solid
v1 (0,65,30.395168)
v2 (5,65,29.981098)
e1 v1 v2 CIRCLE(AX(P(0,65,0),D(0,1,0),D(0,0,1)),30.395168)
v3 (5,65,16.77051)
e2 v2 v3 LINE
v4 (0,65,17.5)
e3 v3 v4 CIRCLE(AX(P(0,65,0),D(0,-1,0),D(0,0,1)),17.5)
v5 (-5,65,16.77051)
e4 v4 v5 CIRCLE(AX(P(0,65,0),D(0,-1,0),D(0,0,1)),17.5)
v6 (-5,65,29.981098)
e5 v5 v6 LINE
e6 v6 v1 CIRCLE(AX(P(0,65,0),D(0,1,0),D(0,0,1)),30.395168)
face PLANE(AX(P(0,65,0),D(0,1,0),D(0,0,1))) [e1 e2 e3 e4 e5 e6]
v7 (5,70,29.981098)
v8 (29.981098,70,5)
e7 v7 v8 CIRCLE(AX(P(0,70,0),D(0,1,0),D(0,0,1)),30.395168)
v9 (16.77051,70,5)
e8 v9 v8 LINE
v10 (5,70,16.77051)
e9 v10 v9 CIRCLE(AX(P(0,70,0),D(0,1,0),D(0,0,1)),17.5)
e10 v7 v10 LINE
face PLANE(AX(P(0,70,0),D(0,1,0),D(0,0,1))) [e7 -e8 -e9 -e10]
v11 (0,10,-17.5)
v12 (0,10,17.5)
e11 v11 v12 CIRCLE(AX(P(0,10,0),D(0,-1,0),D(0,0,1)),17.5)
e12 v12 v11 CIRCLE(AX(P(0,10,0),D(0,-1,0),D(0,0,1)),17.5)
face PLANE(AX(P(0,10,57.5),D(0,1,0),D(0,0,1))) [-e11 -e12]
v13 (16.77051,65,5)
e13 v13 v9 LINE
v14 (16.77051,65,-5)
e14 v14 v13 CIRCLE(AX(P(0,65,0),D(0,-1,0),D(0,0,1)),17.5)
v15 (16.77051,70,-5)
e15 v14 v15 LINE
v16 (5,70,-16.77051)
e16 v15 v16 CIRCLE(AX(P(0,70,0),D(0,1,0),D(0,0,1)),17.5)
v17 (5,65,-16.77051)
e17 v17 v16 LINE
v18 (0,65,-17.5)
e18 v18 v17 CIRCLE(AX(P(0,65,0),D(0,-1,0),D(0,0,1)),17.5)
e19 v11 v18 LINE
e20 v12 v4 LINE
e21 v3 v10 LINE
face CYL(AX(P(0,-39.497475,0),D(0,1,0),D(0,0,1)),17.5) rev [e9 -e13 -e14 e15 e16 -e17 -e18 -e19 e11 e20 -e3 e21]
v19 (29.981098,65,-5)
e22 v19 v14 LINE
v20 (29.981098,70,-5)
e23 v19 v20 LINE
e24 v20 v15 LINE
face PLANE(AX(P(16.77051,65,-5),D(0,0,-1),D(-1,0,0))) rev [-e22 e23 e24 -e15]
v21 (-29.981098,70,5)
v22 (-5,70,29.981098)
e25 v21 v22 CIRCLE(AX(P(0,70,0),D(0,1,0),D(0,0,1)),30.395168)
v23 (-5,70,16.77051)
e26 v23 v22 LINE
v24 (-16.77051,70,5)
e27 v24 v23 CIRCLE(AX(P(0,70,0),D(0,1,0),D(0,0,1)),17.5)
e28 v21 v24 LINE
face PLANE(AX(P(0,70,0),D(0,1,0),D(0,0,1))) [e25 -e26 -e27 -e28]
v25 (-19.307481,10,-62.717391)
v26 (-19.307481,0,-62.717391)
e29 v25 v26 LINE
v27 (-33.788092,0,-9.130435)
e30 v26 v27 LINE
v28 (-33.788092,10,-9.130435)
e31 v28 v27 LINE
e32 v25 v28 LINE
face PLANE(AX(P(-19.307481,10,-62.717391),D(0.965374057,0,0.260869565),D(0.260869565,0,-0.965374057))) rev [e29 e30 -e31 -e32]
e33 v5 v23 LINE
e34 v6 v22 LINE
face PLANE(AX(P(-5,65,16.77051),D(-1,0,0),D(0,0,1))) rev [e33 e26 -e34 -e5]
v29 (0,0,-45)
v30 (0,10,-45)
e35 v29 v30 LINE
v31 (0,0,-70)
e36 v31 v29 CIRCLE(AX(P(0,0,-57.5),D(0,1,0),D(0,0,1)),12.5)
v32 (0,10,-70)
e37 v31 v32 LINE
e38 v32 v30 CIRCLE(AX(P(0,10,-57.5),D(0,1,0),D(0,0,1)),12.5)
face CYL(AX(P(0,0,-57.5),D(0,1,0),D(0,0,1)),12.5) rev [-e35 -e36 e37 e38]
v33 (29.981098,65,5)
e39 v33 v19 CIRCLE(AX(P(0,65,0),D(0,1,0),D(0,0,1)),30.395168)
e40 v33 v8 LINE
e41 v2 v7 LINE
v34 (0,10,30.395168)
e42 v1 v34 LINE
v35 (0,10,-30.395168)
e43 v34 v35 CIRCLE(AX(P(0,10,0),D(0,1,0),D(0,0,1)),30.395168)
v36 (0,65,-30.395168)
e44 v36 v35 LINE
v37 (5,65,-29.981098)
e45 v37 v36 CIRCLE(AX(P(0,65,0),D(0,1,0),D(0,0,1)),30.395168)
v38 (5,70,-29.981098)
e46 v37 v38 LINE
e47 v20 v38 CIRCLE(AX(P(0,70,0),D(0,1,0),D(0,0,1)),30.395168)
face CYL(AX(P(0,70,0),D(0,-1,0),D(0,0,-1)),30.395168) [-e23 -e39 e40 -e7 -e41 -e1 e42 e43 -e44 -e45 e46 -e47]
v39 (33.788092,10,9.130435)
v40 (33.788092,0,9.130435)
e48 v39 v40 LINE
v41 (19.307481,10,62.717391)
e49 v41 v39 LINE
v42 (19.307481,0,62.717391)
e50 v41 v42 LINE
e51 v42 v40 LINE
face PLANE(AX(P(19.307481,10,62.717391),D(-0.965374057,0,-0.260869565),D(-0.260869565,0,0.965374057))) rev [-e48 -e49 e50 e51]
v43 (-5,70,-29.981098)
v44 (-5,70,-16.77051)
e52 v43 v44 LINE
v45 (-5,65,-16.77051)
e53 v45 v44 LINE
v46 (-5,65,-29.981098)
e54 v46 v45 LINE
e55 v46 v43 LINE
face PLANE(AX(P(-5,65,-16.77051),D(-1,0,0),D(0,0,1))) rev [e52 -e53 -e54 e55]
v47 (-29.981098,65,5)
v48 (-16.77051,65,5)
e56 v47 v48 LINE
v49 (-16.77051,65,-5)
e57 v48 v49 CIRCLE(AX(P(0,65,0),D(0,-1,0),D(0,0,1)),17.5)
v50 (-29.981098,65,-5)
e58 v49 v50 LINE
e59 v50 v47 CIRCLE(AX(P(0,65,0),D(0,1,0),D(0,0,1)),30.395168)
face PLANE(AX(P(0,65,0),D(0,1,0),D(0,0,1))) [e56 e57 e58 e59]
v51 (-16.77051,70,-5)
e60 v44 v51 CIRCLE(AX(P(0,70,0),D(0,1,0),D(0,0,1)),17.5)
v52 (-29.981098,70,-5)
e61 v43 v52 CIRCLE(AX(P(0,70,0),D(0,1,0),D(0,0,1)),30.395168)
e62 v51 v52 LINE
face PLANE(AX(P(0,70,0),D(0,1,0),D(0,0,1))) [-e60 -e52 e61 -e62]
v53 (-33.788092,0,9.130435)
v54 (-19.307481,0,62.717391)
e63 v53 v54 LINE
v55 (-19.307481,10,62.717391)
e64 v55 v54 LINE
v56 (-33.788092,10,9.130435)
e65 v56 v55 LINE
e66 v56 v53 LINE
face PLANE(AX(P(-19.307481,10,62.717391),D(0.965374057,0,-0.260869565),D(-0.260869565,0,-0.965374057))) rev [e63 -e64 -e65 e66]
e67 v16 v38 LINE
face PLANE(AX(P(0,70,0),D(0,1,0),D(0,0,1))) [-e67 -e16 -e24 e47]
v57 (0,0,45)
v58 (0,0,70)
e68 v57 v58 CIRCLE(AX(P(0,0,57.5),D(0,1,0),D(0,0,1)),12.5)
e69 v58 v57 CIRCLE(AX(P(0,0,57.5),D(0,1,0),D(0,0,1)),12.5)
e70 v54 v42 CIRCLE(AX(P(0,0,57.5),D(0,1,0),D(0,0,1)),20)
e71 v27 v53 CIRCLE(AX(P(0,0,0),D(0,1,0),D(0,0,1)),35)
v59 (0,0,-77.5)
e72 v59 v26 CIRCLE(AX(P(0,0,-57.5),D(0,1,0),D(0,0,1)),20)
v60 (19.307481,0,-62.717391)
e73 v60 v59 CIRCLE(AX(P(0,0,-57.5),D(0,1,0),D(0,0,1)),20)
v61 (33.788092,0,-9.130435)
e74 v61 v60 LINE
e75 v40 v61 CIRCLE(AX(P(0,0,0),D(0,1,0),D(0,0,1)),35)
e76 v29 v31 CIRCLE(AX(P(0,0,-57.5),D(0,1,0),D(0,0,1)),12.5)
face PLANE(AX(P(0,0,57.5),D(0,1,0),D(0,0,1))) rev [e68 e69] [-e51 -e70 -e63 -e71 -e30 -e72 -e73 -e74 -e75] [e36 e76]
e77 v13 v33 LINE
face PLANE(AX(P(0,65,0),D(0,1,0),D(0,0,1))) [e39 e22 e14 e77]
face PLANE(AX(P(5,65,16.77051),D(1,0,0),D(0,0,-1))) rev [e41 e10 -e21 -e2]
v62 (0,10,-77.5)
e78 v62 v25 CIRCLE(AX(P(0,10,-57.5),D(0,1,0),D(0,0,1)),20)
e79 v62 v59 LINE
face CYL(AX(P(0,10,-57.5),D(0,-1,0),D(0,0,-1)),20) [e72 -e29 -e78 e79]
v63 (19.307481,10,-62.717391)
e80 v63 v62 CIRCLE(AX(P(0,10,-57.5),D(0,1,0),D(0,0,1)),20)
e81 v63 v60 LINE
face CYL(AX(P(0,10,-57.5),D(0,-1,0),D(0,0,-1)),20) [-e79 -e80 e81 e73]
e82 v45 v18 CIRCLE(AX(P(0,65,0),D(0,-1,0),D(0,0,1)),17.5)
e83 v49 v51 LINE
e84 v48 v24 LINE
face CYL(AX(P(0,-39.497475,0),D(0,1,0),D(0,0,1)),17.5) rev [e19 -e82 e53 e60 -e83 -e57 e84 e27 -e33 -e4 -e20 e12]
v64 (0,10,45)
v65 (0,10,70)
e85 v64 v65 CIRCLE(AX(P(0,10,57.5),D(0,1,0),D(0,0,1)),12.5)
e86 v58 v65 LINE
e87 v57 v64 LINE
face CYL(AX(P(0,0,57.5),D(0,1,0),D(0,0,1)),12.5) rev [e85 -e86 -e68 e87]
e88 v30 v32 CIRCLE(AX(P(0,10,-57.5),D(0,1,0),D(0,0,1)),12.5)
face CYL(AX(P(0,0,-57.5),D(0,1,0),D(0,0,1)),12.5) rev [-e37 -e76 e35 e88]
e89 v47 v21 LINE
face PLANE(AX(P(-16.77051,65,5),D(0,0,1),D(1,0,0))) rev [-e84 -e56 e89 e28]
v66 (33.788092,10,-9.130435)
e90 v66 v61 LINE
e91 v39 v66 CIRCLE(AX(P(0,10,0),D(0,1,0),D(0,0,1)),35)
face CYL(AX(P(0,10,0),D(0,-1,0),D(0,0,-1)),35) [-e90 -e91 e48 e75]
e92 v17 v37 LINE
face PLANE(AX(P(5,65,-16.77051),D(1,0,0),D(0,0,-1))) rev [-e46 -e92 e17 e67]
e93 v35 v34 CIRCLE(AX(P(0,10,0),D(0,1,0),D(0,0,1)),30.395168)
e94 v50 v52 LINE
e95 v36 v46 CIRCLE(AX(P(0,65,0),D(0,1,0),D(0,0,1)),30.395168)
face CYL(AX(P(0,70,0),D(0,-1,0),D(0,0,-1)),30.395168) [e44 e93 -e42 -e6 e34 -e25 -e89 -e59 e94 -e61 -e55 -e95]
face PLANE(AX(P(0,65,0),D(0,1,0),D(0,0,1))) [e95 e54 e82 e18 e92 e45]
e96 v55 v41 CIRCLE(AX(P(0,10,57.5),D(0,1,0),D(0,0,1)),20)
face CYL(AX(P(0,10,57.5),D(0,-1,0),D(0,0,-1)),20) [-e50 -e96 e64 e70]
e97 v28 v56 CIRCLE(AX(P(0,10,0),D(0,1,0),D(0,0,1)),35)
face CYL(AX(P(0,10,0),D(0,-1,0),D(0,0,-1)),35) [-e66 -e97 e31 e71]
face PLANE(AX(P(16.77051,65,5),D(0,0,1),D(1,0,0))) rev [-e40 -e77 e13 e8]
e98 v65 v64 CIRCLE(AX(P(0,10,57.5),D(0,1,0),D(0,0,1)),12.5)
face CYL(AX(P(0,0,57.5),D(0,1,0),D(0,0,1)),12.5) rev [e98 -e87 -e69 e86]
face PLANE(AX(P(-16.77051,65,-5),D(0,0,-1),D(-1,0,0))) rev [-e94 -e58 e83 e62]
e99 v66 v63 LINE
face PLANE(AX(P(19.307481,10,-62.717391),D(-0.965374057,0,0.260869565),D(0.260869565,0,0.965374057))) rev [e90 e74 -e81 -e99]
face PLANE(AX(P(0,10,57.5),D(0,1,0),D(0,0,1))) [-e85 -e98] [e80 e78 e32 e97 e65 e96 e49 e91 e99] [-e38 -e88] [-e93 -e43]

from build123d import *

# Parameters (mm, degrees)
BASE_PLATE_DEPTH             = 10
MOUNTING_HOLES_2X_DEPTH      = 86.622718948
MOUNTING_HOLES_2X_DEPTH_BACK = 86.622718948
MOUNTING_HOLES_PROFILE_R     = 12.5
HUB_PROFILE_R                = 30.395167717
HUB_DEPTH                    = 60
BORE_PROFILE_35_R            = 17.5
BORE_35_DEPTH                = 60
CROSS_SLOTS_4X_DEPTH         = 5


with BuildPart() as part:
    # Base Plate Profile → Base Plate (new body)
    with BuildSketch(Plane(origin=(0, 0, 0), x_dir=(1, 0, 0), z_dir=(0, 1, 0))):
        with BuildLine():
            Line((19.30748114, -62.717391304), (33.788091995, -9.130434783))
            ThreePointArc((33.788091995, -9.130434783), (35, 0), (33.788091995, 9.130434783))
            Line((33.788091995, 9.130434783), (19.30748114, 62.717391304))
            ThreePointArc((19.30748114, 62.717391304), (0, 77.5), (-19.30748114, 62.717391304))
            Line((-19.30748114, 62.717391304), (-33.788091995, 9.130434783))
            ThreePointArc((-33.788091995, 9.130434783), (-35, 0), (-33.788091995, -9.130434783))
            Line((-33.788091995, -9.130434783), (-19.30748114, -62.717391304))
            ThreePointArc((-19.30748114, -62.717391304), (0, -77.5), (19.30748114, -62.717391304))
        make_face()
    extrude(amount=BASE_PLATE_DEPTH)

    # Mounting Holes Profile → Mounting Holes 2x (cut, two sides: drawn at the far end of the back side and taken through both)
    with BuildSketch(Plane(origin=(0, 10, 0), x_dir=(1, 0, 0), z_dir=(0, 1, 0)).offset(-MOUNTING_HOLES_2X_DEPTH_BACK)):
        with Locations(Location((0, 57.5, 0), (0, 0, 270))):
            Circle(MOUNTING_HOLES_PROFILE_R)
        with Locations(Location((0, -57.5, 0), (0, 0, 270))):
            Circle(MOUNTING_HOLES_PROFILE_R)
    extrude(amount=MOUNTING_HOLES_2X_DEPTH + MOUNTING_HOLES_2X_DEPTH_BACK, mode=Mode.SUBTRACT)

    # Hub Profile → Hub (add)
    with BuildSketch(Plane(origin=(0, 10, 0), x_dir=(1, 0, 0), z_dir=(0, 1, 0))):
        with Locations(Location((0, 0, 0), (0, 0, 270))):
            Circle(HUB_PROFILE_R)
    extrude(amount=HUB_DEPTH)

    # Bore Profile Ø35 → Bore Ø35 (cut)
    with BuildSketch(Plane(origin=(0, 70, 0), x_dir=(1, 0, 0), z_dir=(0, 1, 0))):
        with Locations(Location((0, 0, 0), (0, 0, 270))):
            Circle(BORE_PROFILE_35_R)
    extrude(amount=-BORE_35_DEPTH, mode=Mode.SUBTRACT)

    # Cross Slots Profile → Cross Slots 4x (cut)
    with BuildSketch(Plane(origin=(0, 70, 0), x_dir=(1, 0, 0), z_dir=(0, 1, 0))):
        with BuildLine():
            Line((-16.770509831, -5), (-29.981097721, -5))
            ThreePointArc((-29.981097721, -5), (-30.395167717, 0), (-29.981097721, 5))
            Line((-29.981097721, 5), (-16.770509831, 5))
            ThreePointArc((-16.770509831, 5), (-17.5, 0), (-16.770509831, -5))
        make_face()
        with BuildLine():
            Line((-5, -16.770509831), (-5, -29.981097721))
            ThreePointArc((-5, -29.981097721), (0, -30.395167717), (5, -29.981097721))
            Line((5, -29.981097721), (5, -16.770509831))
            ThreePointArc((5, -16.770509831), (0, -17.5), (-5, -16.770509831))
        make_face()
        with BuildLine():
            Line((-5, 16.770509831), (-5, 29.981097721))
            ThreePointArc((-5, 29.981097721), (0, 30.395167717), (5, 29.981097721))
            Line((5, 29.981097721), (5, 16.770509831))
            ThreePointArc((5, 16.770509831), (0, 17.5), (-5, 16.770509831))
        make_face()
        with BuildLine():
            Line((16.770509831, 5), (29.981097721, 5))
            ThreePointArc((29.981097721, 5), (30.395167717, 0), (29.981097721, -5))
            Line((29.981097721, -5), (16.770509831, -5))
            ThreePointArc((16.770509831, -5), (17.5, 0), (16.770509831, 5))
        make_face()
    extrude(amount=-CROSS_SLOTS_4X_DEPTH, mode=Mode.SUBTRACT)


solid = part.part
